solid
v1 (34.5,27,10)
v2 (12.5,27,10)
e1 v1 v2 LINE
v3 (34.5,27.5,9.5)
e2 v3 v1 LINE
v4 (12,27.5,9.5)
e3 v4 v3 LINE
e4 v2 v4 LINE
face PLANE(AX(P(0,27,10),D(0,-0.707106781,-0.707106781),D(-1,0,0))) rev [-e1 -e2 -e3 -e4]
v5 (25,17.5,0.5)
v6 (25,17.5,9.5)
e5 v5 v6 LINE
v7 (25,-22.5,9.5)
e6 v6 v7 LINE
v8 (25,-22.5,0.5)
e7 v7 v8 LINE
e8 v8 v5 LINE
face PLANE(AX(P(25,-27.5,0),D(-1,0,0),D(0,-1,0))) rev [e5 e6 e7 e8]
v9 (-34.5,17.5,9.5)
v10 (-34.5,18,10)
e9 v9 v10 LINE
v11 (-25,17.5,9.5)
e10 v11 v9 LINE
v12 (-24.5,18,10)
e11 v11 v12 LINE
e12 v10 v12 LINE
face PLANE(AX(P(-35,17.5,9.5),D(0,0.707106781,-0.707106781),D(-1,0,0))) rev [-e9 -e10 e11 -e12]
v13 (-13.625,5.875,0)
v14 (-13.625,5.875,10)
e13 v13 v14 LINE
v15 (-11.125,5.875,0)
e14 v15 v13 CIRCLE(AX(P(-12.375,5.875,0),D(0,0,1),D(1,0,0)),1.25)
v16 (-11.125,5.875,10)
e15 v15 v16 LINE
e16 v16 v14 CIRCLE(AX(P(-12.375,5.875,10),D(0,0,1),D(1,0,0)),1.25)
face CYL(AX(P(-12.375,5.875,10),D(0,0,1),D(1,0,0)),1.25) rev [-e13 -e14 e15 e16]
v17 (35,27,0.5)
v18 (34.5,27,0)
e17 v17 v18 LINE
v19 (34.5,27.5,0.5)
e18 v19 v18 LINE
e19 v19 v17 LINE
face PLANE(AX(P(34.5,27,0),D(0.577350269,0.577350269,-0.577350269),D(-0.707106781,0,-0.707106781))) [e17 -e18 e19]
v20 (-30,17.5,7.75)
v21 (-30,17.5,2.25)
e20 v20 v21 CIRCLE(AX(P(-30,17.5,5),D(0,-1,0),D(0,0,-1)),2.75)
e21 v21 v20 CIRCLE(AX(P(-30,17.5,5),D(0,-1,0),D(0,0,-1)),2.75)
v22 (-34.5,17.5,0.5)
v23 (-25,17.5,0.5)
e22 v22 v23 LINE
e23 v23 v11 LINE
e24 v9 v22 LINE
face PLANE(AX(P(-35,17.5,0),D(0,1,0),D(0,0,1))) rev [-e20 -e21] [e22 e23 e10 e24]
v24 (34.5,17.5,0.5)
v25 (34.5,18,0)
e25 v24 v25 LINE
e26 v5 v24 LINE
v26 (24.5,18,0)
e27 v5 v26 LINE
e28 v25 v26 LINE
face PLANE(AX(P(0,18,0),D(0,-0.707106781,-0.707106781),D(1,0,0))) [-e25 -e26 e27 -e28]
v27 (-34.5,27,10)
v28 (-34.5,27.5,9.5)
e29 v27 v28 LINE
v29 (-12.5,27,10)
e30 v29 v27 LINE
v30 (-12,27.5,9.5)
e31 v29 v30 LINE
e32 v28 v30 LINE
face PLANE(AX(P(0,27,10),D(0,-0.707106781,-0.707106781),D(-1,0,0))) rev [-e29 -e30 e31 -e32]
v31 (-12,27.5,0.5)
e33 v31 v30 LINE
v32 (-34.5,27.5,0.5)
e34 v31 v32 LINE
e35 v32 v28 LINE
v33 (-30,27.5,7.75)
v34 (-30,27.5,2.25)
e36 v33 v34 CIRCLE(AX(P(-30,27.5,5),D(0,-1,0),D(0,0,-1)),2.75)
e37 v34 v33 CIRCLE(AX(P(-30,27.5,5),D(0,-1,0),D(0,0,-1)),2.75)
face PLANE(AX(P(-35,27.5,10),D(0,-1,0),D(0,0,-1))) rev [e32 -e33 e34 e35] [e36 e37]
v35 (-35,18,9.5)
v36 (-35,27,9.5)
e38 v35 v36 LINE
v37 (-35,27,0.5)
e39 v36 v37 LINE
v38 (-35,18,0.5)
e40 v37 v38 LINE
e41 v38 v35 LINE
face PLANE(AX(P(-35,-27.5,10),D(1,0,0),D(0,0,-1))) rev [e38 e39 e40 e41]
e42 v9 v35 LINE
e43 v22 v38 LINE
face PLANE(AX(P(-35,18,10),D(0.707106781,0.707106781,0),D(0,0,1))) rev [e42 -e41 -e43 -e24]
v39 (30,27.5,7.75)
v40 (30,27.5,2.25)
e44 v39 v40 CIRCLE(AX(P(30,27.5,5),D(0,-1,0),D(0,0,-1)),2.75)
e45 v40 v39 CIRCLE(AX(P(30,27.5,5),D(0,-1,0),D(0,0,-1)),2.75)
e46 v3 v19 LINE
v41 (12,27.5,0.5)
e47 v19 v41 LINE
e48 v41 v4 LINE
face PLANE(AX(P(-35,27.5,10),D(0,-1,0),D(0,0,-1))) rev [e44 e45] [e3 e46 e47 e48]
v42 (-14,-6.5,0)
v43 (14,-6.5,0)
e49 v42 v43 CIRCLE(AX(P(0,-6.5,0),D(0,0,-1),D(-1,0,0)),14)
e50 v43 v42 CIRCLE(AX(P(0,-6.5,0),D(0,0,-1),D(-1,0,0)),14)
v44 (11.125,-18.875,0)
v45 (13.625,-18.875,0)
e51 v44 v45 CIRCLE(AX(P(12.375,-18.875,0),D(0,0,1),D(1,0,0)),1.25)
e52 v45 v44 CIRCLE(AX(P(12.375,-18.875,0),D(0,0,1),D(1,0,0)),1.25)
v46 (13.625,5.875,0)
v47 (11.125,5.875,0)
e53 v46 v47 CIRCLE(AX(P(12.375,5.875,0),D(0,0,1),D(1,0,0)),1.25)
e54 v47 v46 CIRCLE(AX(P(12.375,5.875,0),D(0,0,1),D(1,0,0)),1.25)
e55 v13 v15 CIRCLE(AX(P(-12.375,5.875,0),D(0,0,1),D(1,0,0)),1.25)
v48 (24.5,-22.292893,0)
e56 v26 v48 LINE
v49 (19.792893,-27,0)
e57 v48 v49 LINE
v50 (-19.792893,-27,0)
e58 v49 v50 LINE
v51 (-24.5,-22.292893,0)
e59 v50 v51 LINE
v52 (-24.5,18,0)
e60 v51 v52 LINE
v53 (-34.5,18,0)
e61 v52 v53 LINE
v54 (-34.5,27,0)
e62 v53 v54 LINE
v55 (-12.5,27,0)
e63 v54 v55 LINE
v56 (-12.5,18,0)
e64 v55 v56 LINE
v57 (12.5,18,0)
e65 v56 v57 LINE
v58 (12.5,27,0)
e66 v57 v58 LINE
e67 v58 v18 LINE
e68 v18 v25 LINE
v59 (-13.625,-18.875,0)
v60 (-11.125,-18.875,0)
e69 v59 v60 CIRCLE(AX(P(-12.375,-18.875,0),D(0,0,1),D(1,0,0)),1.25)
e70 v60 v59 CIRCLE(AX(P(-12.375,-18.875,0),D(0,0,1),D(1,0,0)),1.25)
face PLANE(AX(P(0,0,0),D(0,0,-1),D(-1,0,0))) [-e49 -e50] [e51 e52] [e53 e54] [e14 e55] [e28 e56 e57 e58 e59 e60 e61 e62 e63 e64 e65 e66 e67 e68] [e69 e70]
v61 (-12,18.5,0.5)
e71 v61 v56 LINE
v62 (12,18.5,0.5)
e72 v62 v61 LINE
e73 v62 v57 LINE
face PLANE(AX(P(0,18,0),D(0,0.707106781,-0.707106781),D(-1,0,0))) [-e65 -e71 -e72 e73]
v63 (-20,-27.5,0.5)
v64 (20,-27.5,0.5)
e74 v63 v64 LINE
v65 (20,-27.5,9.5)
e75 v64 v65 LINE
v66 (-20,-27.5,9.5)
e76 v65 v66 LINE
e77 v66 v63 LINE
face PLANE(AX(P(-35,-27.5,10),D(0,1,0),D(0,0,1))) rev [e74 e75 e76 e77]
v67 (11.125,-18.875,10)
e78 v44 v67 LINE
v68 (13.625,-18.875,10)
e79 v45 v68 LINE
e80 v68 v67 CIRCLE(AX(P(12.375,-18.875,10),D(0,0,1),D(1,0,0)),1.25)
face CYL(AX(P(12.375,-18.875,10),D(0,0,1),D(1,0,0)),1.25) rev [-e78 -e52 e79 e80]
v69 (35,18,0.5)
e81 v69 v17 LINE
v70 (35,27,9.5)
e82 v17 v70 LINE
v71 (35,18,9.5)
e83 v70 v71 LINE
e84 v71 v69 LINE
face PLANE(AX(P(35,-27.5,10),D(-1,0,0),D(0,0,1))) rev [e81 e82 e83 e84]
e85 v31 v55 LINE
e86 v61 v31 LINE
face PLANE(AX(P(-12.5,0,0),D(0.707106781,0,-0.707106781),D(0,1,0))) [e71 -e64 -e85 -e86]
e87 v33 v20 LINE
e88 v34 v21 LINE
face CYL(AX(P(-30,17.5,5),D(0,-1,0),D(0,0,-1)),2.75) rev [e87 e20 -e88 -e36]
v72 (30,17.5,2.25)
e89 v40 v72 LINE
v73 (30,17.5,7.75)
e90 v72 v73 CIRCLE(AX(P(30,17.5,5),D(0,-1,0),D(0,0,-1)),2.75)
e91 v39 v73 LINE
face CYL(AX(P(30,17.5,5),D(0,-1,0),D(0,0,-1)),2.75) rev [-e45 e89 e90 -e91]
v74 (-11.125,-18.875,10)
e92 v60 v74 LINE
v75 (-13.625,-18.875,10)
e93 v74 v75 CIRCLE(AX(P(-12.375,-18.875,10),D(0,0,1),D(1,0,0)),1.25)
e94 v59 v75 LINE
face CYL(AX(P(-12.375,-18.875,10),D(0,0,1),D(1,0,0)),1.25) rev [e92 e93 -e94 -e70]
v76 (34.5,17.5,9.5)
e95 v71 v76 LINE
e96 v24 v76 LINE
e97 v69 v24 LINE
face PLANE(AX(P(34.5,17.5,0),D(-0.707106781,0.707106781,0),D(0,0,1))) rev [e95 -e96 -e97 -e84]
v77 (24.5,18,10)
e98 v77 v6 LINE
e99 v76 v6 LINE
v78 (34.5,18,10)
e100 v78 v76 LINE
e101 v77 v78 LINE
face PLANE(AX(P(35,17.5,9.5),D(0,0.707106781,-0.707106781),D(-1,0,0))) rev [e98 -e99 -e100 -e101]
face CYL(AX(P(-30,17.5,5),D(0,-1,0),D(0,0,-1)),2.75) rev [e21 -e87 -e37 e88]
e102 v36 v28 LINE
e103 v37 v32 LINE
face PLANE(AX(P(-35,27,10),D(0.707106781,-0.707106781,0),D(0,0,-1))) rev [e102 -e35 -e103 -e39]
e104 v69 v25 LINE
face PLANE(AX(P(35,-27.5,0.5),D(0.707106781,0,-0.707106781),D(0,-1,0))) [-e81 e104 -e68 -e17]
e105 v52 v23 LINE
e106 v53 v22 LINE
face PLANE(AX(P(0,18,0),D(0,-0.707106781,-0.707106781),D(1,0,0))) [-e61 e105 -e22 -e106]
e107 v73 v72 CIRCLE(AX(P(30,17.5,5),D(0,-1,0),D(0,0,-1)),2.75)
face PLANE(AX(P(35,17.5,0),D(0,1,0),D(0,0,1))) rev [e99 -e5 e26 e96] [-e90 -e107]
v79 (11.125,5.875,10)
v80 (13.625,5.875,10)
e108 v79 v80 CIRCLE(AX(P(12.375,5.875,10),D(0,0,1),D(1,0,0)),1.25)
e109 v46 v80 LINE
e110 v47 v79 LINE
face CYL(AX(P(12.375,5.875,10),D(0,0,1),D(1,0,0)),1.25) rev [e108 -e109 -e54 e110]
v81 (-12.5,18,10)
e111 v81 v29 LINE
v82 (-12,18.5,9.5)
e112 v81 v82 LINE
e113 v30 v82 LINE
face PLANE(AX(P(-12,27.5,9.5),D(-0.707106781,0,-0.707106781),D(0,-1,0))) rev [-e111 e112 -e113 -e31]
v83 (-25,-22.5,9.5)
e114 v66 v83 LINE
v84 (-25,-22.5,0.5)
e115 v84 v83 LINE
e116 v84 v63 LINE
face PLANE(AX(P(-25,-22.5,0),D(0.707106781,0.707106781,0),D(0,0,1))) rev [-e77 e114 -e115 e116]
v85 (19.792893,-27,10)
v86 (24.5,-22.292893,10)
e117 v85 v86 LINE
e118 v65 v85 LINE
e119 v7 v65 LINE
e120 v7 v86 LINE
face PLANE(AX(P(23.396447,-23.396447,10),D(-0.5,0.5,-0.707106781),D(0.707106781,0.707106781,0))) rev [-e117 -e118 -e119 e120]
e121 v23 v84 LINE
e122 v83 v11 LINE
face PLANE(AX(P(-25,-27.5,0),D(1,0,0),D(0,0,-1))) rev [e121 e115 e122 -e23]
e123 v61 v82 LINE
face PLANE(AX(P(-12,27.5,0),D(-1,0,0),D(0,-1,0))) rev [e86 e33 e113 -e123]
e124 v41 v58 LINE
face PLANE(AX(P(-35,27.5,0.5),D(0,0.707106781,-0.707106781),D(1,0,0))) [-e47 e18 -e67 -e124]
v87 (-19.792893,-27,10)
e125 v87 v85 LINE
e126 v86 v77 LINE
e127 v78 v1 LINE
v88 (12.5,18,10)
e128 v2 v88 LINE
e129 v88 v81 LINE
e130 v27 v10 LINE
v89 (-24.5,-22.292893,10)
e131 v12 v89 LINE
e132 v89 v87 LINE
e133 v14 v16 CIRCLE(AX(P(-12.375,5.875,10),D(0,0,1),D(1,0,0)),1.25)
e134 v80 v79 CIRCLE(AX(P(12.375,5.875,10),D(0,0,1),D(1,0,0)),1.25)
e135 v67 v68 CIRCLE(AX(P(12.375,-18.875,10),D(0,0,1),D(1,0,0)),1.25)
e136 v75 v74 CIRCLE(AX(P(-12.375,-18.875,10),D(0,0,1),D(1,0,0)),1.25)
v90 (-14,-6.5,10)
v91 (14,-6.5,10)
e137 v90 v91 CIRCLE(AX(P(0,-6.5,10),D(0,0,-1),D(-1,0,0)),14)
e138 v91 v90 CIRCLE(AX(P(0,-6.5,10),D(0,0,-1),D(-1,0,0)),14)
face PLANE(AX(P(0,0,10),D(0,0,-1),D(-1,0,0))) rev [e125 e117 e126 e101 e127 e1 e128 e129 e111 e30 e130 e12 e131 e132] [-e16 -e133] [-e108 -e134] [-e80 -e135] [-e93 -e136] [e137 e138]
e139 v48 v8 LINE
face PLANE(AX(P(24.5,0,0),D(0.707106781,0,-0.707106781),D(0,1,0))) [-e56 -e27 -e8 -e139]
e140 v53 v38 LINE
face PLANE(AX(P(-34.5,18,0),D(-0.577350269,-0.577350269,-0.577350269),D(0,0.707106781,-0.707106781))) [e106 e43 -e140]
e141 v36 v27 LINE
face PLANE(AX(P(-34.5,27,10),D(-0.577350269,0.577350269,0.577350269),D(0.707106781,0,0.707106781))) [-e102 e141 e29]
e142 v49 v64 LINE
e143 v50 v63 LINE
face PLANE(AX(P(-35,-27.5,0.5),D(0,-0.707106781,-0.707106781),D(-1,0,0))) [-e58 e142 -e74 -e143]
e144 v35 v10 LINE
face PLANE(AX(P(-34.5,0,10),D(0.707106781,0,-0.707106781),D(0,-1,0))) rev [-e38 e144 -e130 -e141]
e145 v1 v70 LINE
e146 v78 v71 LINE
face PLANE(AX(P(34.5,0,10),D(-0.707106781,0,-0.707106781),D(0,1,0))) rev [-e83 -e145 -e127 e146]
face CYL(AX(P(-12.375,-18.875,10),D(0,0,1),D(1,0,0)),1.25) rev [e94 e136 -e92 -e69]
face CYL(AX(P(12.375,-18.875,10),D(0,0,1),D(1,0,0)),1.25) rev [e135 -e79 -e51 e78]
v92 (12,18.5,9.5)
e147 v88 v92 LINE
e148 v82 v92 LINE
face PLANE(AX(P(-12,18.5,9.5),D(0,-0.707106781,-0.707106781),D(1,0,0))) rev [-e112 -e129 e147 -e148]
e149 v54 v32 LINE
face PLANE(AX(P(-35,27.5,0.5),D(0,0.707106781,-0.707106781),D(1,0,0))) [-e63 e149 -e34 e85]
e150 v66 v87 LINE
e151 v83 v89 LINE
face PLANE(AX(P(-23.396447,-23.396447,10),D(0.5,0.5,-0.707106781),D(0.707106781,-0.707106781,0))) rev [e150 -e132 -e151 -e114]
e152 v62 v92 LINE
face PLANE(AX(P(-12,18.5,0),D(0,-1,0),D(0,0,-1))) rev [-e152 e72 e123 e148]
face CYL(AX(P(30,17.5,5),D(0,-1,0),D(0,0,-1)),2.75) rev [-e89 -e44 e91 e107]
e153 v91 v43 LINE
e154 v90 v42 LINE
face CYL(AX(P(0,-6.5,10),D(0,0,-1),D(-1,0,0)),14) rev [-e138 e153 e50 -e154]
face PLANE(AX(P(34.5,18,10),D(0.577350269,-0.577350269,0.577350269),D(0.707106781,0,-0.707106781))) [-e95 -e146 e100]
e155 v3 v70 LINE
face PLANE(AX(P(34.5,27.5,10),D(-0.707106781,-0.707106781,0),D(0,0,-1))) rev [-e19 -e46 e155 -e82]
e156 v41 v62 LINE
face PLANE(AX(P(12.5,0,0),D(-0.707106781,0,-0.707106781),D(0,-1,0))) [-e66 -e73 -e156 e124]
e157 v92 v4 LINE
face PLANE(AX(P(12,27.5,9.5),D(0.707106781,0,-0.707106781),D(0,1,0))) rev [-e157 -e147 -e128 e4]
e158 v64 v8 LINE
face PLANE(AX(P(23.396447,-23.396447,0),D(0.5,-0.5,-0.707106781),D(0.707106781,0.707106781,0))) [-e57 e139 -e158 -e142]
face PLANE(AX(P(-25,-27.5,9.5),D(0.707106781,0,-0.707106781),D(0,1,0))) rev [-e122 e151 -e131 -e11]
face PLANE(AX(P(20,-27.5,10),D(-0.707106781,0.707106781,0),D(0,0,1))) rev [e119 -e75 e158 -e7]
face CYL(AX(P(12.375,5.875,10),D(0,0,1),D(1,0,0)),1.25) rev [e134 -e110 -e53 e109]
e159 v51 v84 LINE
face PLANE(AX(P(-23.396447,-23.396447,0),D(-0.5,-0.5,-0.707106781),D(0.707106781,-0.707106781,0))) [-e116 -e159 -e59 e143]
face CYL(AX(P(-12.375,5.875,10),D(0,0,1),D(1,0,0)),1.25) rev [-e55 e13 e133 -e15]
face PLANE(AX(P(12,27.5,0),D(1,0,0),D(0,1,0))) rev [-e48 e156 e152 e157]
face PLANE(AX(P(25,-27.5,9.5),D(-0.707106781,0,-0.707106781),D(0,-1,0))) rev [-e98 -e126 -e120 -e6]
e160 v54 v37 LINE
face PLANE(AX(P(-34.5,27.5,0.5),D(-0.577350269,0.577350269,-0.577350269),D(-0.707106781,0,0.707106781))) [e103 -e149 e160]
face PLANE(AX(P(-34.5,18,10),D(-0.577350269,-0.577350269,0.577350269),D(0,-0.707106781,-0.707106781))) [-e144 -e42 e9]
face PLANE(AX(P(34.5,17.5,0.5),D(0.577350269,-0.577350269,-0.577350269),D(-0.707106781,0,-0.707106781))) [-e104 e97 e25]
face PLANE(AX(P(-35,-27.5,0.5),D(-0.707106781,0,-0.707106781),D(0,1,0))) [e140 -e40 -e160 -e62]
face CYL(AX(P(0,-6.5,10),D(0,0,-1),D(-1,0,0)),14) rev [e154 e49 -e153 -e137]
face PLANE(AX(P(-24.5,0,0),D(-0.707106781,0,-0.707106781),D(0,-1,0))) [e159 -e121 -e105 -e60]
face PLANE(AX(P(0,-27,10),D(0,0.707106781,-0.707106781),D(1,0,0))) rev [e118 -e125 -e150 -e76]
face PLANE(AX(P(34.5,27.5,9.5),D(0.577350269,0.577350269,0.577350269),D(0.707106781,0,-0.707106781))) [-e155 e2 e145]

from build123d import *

# Parameters (mm, degrees)
SKETCH_1_W              = 70
SKETCH_1_H              = 55
EXTRUDE_1_DEPTH         = 10
SKETCH_2_W              = 10
SKETCH_2_H              = 45
CUT_EXTRUDE_1_DEPTH     = 46.620718977
SKETCH_3_R              = 14
CUT_EXTRUDE_2_DEPTH     = 46.620718977
HOLE_WIZARD_M3_1_D      = 2.5
HOLE_WIZARD_5_5_5_5_1_D = 5.5
CHAMFER_1_SIZE          = 5
SKETCH_12_W             = 24
SKETCH_12_H             = 9
CUT_EXTRUDE_3_DEPTH     = 46.620718977
CHAMFER_2_SIZE          = 0.5


with BuildPart() as part:
    # 草图1 → 凸台-拉伸1 (new body)
    with BuildSketch(Plane.XY):
        Rectangle(SKETCH_1_W, SKETCH_1_H)
    extrude(amount=EXTRUDE_1_DEPTH)

    # 草图2 → 切除-拉伸1 (cut, through all)
    with BuildSketch(Plane.XY.offset(10)):
        with Locations((-30, -5)):
            Rectangle(SKETCH_2_W, SKETCH_2_H)
        with Locations((30, -5)):
            Rectangle(SKETCH_2_W, SKETCH_2_H)
    extrude(amount=-CUT_EXTRUDE_1_DEPTH, mode=Mode.SUBTRACT)

    # 草图3 → 切除-拉伸2 (cut, through all)
    with BuildSketch(Plane(origin=(0, 0, 0), x_dir=(-1, 0, 0), z_dir=(0, 0, -1))):
        with Locations((0, -6.5)):
            Circle(SKETCH_3_R)
    extrude(amount=-CUT_EXTRUDE_2_DEPTH, mode=Mode.SUBTRACT)

    # M3 螺纹孔1 (through all)
    with Locations(Plane.XY.offset(10)):
        with Locations((12.375, -18.875), (-12.375, -18.875), (-12.375, 5.875), (12.375, 5.875)):
            Hole(HOLE_WIZARD_M3_1_D / 2)

    # Ø5.5 (5.5) 直径孔1 (through all)
    with Locations(Plane(origin=(0, 17.5, 0), x_dir=(-1, 0, 0), z_dir=(0, -1, 0))):
        with Locations((-30, -5), (30, -5)):
            Hole(HOLE_WIZARD_5_5_5_5_1_D / 2)

    # 倒角1
    chamfer_1_edges = [part.edges().sort_by_distance(p)[0] for p in [
        (-25, -27.5, 5),
        (25, -27.5, 5),
    ]]
    chamfer(chamfer_1_edges, length=CHAMFER_1_SIZE)

    # 草图12 → 切除-拉伸3 (cut, through all)
    with BuildSketch(Plane.XY.offset(10)):
        with Locations((0, 23)):
            Rectangle(SKETCH_12_W, SKETCH_12_H)
    extrude(amount=-CUT_EXTRUDE_3_DEPTH, mode=Mode.SUBTRACT)

    # 倒角2
    chamfer_2_edges = [part.edges().sort_by_distance(p)[0] for p in [
        (-35, 22.5, 10),
        (0, 18.5, 10),
        (12, 23, 10),
        (-30, 17.5, 0),
        (-35, 17.5, 5),
        (-30, 17.5, 10),
        (35, 22.5, 0),
        (35, 22.5, 10),
        (25, -2.5, 0),
        (30, 17.5, 0),
        (35, 17.5, 5),
        (30, 17.5, 10),
        (25, -2.5, 10),
        (-35, 22.5, 0),
        (23.5, 27.5, 0),
        (23.5, 27.5, 10),
        (-35, 27.5, 5),
        (35, 27.5, 5),
        (-25, -2.5, 10),
        (-25, -2.5, 0),
        (0, -27.5, 10),
        (22.5, -25, 10),
        (-22.5, -25, 10),
        (0, -27.5, 0),
        (22.5, -25, 0),
        (-22.5, -25, 0),
        (-23.5, 27.5, 0),
        (-23.5, 27.5, 10),
        (-12, 23, 0),
        (12, 23, 0),
        (0, 18.5, 0),
        (-12, 23, 10),
    ]]
    chamfer(chamfer_2_edges, length=CHAMFER_2_SIZE)


solid = part.part
